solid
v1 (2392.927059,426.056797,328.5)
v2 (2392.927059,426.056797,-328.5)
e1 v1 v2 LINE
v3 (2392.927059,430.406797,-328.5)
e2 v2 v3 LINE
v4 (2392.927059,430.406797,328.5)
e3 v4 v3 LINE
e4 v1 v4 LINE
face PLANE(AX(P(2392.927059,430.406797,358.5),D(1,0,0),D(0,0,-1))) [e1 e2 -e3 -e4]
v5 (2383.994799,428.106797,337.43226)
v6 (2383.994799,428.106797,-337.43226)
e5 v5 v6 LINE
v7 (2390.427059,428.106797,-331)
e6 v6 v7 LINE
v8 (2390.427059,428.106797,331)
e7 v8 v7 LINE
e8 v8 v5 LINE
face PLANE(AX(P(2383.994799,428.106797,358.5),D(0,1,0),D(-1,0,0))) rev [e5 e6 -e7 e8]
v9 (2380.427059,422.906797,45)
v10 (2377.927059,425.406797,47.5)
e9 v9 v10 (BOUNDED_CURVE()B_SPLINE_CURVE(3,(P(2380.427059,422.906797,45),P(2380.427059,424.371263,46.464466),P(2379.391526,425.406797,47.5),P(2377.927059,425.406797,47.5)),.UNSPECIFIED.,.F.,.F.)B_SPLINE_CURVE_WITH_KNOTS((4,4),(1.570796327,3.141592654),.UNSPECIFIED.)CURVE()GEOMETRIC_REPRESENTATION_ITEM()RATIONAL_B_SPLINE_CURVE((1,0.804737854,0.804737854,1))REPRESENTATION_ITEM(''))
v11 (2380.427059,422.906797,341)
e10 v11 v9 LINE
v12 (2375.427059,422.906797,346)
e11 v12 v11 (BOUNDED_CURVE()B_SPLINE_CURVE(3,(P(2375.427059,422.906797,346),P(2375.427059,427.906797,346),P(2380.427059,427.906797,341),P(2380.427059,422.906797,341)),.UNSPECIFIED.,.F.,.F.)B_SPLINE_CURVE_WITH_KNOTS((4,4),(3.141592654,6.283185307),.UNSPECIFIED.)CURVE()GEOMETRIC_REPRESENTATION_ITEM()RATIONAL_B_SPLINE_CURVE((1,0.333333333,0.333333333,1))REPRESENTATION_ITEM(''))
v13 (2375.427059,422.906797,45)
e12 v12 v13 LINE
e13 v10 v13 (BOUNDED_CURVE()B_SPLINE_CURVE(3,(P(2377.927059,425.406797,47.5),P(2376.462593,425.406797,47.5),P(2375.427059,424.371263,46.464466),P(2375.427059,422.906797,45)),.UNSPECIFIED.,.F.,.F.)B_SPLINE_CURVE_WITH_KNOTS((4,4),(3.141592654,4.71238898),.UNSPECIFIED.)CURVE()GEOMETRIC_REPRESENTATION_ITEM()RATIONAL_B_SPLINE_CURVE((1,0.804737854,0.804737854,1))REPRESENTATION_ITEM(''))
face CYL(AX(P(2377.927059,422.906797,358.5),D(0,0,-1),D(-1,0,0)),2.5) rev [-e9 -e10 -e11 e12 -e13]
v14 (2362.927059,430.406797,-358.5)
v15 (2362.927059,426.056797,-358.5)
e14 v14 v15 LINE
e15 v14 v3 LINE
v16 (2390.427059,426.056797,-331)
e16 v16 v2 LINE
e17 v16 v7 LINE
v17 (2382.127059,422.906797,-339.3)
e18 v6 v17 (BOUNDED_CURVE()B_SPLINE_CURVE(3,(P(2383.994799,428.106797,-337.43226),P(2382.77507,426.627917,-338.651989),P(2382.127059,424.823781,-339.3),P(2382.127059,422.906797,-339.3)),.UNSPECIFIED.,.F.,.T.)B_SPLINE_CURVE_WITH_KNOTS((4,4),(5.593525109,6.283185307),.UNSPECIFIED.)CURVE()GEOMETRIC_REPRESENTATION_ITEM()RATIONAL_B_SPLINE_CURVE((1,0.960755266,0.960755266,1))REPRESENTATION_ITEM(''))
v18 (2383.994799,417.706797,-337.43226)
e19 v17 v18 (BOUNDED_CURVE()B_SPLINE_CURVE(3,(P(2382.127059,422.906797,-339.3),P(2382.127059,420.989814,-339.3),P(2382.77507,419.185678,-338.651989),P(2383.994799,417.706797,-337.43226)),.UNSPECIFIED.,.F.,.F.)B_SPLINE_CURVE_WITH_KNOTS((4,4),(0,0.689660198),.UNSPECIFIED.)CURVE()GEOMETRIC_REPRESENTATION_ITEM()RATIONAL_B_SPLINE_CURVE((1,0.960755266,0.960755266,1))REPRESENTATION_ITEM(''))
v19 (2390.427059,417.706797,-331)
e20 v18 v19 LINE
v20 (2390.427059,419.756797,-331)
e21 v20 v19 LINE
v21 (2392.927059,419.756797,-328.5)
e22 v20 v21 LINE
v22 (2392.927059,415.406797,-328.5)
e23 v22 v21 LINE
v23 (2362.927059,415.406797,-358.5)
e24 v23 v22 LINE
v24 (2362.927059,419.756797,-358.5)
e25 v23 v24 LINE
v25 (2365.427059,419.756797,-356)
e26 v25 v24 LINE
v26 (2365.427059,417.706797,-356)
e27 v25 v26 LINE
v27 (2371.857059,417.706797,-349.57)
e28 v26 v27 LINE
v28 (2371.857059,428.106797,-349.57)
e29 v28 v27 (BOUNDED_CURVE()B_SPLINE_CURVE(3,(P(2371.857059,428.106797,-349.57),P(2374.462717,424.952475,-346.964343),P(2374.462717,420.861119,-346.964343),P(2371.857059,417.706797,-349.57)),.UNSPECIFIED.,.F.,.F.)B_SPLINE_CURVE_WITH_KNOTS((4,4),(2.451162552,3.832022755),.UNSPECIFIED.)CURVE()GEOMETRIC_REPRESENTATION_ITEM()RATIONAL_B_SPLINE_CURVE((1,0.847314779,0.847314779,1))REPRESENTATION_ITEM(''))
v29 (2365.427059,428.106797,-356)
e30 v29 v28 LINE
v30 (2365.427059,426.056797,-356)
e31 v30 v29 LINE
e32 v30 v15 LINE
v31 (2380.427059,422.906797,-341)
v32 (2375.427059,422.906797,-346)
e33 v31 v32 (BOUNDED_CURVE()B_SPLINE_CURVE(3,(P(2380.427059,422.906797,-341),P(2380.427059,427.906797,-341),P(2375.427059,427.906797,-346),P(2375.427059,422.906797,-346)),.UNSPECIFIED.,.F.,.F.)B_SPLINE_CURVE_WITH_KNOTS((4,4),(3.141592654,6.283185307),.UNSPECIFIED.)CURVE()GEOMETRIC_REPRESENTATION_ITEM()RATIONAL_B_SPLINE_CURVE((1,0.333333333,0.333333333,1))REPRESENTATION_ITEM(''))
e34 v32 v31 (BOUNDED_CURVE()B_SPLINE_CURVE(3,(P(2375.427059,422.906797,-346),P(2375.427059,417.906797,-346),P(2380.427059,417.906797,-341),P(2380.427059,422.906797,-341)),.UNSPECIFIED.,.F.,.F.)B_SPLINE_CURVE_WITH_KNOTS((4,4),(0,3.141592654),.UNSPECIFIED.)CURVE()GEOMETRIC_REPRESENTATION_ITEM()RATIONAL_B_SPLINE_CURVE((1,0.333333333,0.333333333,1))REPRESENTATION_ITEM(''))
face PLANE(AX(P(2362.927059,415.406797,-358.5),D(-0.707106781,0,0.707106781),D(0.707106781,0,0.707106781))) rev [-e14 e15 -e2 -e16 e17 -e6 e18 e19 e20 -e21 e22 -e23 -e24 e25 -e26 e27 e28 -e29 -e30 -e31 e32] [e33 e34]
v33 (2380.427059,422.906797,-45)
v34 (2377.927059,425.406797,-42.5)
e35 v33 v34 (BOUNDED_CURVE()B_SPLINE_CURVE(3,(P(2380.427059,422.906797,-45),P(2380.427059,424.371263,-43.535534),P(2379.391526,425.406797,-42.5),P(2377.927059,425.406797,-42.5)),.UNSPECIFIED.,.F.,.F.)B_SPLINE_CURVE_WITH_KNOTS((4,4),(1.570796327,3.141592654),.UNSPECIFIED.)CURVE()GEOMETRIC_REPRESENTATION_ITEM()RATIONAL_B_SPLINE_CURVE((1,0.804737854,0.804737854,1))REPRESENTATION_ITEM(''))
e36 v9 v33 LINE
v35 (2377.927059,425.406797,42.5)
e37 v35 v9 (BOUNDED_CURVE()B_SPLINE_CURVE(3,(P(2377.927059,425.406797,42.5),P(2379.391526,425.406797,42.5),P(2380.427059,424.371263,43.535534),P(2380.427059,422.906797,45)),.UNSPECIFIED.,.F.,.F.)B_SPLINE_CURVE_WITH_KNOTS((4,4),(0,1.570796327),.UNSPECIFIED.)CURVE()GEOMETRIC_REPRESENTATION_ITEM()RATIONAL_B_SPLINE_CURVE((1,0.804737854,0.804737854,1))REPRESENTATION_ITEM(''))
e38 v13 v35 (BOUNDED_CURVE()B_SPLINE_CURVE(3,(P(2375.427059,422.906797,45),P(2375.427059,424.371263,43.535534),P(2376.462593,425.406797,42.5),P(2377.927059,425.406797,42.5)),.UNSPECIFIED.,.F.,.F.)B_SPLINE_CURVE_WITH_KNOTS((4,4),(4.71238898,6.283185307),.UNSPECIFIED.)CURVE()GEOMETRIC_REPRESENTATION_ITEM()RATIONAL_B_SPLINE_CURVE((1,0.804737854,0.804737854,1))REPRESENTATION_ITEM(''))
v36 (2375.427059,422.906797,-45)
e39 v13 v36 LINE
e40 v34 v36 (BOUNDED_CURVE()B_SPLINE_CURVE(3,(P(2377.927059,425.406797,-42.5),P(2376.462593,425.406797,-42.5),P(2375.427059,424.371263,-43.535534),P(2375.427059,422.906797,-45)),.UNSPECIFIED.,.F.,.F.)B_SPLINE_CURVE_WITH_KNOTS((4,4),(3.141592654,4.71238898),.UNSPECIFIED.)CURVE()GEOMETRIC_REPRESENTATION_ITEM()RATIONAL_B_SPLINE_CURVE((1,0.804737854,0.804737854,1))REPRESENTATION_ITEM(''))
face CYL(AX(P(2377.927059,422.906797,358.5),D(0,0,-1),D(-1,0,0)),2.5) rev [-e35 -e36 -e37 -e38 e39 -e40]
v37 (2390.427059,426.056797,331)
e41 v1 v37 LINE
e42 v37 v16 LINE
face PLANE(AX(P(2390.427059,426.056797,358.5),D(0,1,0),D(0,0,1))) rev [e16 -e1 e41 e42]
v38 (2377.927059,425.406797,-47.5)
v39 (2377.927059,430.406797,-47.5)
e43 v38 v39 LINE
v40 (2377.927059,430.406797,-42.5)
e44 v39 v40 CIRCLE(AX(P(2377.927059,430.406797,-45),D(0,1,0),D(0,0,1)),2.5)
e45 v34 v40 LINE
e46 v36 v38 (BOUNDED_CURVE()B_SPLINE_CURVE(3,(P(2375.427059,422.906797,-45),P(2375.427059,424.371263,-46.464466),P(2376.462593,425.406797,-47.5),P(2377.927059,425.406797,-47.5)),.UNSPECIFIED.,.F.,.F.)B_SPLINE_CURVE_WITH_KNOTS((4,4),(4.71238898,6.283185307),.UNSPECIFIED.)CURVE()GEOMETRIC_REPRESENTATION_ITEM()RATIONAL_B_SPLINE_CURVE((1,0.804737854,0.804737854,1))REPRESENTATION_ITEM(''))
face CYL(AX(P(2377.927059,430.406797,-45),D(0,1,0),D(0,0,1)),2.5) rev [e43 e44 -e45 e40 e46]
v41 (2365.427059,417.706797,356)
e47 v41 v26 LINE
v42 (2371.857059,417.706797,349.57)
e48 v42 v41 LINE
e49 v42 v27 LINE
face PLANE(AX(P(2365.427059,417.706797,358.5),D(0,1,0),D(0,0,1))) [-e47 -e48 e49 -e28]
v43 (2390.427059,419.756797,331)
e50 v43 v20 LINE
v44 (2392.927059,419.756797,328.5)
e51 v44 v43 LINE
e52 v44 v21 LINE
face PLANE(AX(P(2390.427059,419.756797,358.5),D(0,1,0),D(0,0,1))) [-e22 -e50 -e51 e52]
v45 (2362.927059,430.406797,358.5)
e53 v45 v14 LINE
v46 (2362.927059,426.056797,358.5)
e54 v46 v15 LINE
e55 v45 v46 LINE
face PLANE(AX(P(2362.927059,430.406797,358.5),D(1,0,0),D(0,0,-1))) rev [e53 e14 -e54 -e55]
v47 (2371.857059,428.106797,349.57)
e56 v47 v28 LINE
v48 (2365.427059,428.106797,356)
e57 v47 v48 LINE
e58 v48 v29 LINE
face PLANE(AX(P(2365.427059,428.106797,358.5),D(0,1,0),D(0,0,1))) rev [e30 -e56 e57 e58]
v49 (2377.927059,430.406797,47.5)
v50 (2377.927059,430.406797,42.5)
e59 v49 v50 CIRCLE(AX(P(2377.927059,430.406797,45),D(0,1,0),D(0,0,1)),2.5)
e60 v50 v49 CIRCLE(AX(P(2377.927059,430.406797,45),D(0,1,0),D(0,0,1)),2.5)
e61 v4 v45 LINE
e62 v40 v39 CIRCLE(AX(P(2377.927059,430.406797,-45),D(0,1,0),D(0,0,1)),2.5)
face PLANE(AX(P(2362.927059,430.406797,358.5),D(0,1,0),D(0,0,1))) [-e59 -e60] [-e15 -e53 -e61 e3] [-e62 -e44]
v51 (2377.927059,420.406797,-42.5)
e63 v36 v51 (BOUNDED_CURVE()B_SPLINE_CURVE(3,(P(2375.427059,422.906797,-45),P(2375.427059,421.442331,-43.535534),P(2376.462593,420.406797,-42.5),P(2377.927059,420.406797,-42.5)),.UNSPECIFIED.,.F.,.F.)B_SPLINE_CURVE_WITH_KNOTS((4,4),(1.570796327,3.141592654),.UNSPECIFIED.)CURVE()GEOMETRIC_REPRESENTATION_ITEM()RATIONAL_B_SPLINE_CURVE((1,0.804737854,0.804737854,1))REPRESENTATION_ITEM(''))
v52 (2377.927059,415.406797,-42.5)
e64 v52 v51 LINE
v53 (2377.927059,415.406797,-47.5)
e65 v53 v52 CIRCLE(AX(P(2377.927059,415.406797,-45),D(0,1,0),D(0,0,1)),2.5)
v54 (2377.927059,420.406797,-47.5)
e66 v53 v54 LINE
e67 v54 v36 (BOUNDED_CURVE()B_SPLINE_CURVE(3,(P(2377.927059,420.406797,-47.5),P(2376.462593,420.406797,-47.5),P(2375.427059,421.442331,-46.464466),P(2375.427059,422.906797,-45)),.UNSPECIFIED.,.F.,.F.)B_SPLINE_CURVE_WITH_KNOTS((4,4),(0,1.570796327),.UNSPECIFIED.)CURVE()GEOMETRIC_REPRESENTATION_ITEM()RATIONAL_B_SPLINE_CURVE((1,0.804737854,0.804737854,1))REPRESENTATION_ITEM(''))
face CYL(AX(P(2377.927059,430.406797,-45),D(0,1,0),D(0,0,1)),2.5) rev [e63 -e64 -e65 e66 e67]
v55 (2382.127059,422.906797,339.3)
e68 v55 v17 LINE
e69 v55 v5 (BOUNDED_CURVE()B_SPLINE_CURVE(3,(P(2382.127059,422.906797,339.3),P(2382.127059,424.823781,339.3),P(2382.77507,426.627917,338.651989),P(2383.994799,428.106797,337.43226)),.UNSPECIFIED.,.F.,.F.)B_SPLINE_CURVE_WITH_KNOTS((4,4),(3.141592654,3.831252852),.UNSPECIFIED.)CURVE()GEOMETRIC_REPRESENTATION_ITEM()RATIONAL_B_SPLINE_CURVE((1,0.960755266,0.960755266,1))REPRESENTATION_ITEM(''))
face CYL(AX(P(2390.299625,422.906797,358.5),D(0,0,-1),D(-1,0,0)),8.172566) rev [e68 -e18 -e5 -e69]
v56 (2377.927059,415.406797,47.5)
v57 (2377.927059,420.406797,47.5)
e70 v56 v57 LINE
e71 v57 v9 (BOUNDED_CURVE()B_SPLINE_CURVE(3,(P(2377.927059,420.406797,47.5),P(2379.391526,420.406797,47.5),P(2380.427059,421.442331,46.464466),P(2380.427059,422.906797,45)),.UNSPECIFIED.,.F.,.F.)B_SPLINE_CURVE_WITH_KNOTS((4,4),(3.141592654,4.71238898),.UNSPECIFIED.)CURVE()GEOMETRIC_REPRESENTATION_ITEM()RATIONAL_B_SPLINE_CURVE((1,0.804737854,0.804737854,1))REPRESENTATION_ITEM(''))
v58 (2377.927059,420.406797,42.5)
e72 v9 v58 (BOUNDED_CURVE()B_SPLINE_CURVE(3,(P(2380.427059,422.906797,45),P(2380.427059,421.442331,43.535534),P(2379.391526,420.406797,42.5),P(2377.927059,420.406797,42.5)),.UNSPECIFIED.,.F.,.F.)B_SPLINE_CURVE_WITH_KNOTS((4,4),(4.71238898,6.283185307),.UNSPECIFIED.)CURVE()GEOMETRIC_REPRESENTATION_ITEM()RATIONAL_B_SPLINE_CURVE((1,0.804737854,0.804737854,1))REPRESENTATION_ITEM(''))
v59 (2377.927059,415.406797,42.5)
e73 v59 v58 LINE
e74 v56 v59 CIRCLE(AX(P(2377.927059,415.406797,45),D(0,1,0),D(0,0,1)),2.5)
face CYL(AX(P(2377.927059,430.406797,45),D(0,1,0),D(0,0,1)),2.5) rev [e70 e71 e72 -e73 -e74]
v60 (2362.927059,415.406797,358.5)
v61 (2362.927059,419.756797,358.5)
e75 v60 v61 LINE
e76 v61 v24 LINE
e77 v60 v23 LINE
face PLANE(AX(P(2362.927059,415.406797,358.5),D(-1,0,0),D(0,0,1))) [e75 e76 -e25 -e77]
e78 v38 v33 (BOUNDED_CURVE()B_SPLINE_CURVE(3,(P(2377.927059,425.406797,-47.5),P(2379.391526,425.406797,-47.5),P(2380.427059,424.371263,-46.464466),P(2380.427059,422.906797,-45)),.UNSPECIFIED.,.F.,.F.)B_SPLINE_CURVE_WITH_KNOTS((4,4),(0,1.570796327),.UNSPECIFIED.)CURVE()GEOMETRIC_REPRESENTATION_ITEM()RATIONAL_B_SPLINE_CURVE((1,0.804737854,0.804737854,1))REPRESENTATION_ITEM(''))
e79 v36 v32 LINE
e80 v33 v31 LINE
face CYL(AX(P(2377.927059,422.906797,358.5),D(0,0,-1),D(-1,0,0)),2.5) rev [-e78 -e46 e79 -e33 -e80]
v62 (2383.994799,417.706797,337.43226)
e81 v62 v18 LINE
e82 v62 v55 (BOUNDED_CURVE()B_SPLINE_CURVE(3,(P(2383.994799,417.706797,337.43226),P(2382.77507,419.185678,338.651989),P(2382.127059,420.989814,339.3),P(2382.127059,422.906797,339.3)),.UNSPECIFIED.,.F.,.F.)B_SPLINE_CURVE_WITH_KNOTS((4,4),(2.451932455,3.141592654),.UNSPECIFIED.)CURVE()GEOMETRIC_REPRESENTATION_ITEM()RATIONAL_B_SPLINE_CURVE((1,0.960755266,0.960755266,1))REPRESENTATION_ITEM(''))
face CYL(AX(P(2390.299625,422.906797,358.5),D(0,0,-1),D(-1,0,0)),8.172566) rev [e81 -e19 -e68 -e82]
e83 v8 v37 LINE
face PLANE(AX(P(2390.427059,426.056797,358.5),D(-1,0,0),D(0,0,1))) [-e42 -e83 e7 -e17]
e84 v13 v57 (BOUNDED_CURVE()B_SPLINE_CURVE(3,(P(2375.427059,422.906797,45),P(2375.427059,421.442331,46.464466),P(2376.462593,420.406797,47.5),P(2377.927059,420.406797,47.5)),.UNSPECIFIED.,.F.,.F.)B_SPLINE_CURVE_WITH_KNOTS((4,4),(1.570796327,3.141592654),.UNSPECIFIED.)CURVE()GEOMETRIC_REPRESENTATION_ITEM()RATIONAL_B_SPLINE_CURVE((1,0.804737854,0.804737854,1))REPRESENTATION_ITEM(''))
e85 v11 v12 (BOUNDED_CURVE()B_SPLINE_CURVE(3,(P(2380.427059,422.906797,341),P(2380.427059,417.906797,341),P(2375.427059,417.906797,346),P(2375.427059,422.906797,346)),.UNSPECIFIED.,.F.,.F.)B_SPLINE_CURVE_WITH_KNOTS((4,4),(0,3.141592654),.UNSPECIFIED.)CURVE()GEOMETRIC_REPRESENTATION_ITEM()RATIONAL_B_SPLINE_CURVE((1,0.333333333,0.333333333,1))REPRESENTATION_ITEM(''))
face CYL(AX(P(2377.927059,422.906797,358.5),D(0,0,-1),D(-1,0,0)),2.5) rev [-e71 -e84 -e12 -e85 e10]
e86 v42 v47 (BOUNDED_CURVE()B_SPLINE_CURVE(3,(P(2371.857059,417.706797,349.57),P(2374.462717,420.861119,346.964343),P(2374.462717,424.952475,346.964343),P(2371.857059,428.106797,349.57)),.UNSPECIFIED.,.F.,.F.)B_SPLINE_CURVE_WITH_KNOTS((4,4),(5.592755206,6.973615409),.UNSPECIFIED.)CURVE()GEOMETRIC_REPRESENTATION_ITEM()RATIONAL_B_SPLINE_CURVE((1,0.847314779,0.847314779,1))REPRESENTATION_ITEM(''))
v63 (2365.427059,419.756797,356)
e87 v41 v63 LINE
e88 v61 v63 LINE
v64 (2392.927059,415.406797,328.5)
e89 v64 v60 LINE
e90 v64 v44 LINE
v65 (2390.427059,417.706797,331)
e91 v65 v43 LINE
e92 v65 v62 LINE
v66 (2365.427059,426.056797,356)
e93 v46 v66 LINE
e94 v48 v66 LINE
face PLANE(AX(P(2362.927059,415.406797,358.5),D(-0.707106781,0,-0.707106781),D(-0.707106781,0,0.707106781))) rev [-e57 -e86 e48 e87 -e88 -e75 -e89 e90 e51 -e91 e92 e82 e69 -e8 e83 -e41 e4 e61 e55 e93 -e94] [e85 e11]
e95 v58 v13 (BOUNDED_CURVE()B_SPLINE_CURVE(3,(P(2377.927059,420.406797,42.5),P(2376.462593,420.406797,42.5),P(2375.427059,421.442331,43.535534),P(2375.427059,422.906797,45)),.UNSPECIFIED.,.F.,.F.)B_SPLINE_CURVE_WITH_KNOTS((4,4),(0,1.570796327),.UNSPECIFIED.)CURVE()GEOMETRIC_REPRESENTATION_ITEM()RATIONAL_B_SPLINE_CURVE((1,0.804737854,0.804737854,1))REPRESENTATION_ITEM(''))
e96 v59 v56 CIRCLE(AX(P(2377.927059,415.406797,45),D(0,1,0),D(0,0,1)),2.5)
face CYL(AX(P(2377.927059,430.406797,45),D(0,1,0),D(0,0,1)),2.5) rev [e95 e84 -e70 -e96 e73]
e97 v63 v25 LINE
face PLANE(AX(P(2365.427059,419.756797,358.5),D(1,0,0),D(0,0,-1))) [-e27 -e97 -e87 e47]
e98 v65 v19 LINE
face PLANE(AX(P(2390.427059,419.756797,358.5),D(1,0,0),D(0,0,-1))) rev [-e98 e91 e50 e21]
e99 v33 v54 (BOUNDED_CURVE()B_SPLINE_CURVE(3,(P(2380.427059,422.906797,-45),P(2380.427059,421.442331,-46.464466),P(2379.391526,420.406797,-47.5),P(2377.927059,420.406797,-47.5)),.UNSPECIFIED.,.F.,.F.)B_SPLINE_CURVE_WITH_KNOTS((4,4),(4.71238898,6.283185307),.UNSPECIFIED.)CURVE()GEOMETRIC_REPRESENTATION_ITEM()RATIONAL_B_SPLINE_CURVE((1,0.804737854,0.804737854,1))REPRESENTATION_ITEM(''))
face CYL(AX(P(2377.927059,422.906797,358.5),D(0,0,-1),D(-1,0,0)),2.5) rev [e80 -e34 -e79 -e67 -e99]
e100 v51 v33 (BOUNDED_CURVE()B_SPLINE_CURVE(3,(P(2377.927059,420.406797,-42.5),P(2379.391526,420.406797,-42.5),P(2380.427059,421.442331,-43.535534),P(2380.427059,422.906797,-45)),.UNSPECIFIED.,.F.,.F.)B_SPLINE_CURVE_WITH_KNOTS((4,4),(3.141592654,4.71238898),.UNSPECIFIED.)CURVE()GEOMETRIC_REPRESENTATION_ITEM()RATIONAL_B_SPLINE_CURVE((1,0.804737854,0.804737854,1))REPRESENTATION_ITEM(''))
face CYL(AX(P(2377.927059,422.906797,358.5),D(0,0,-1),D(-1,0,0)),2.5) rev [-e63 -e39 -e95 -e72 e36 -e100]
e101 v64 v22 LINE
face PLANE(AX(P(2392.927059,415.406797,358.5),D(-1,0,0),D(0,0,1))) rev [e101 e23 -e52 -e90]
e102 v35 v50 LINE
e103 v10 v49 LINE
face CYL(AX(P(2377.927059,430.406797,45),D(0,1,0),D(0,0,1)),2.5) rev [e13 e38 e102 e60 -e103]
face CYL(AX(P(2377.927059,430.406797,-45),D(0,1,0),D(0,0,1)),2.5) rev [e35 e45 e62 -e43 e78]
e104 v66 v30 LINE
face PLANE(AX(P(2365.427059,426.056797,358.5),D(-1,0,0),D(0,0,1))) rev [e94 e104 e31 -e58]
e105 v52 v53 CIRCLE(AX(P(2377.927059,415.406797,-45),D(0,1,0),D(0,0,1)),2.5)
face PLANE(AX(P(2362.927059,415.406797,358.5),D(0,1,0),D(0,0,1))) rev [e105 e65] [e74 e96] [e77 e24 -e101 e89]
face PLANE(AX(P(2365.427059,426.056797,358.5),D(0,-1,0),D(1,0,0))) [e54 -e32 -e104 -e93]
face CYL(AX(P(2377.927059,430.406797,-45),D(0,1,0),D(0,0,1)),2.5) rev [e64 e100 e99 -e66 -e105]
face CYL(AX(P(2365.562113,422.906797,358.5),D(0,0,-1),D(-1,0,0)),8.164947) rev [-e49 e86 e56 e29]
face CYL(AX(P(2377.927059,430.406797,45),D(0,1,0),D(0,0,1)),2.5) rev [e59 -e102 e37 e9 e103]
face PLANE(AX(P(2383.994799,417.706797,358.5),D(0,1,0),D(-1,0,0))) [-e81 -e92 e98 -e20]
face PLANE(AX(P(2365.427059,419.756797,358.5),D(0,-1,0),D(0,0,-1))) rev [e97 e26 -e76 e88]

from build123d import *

# Parameters (mm, degrees)
MODEL_R             = 2.5
EXTRUDE_1_DEPTH     = 358.5
CUT_EXTRUDE_1_DEPTH = 2420.679144403
HOLE_WIZARD_M6_1_D  = 5


with BuildPart() as part:
    # Model → 凸台-拉伸1 (new, symmetric)
    with BuildSketch(Plane.XY):
        with BuildLine():
            Line((2390.427059452, 419.756797217), (2392.927059452, 419.756797217))
            Line((2392.927059452, 419.756797217), (2392.927059452, 415.406797217))
            Line((2392.927059452, 415.406797217), (2362.927059452, 415.406797217))
            Line((2362.927059452, 415.406797217), (2362.927059452, 419.756797217))
            Line((2362.927059452, 419.756797217), (2365.427059452, 419.756797217))
            Line((2365.427059452, 419.756797217), (2365.427059452, 417.706797217))
            Line((2365.427059452, 417.706797217), (2371.857059452, 417.706797217))
            ThreePointArc((2371.857059452, 417.706797217), (2373.727059452, 422.906797217), (2371.857059452, 428.106797217))
            Line((2371.857059452, 428.106797217), (2365.427059452, 428.106797217))
            Line((2365.427059452, 428.106797217), (2365.427059452, 426.056797217))
            Line((2365.427059452, 426.056797217), (2362.927059452, 426.056797217))
            Line((2362.927059452, 426.056797217), (2362.927059452, 430.406797217))
            Line((2362.927059452, 430.406797217), (2392.927059452, 430.406797217))
            Line((2392.927059452, 430.406797217), (2392.927059452, 426.056797217))
            Line((2392.927059452, 426.056797217), (2390.427059452, 426.056797217))
            Line((2390.427059452, 426.056797217), (2390.427059452, 428.106797217))
            Line((2390.427059452, 428.106797217), (2383.994799144, 428.106797217))
            ThreePointArc((2383.994799144, 428.106797217), (2382.127059452, 422.906797217), (2383.994799144, 417.706797217))
            Line((2383.994799144, 417.706797217), (2390.427059452, 417.706797217))
            Line((2390.427059452, 417.706797217), (2390.427059452, 419.756797217))
        make_face()
        with Locations((2377.927059452, 422.906797217)):
            Circle(MODEL_R, mode=Mode.SUBTRACT)
    extrude(amount=EXTRUDE_1_DEPTH, both=True)

    # 草图1 → 切除-拉伸1 (cut, through all)
    with BuildSketch(Plane(origin=(0, 430.406797217, 0), x_dir=(1, 0, 0), z_dir=(0, 1, 0))):
        Polygon((2362.927059452, 358.5), (2392.927059452, 328.5), (2392.927059452, 358.5), align=None)
        Polygon((2362.927059452, -358.5), (2392.927059452, -328.5), (2392.927059452, -358.5), align=None)
    extrude(amount=-CUT_EXTRUDE_1_DEPTH, mode=Mode.SUBTRACT)

    # M6 螺纹孔1 (through all)
    with Locations(Plane(origin=(0, 430.406797217, 0), x_dir=(1, 0, 0), z_dir=(0, 1, 0))):
        with Locations((2377.927059452, 45), (2377.927059452, -45)):
            Hole(HOLE_WIZARD_M6_1_D / 2)


solid = part.part
